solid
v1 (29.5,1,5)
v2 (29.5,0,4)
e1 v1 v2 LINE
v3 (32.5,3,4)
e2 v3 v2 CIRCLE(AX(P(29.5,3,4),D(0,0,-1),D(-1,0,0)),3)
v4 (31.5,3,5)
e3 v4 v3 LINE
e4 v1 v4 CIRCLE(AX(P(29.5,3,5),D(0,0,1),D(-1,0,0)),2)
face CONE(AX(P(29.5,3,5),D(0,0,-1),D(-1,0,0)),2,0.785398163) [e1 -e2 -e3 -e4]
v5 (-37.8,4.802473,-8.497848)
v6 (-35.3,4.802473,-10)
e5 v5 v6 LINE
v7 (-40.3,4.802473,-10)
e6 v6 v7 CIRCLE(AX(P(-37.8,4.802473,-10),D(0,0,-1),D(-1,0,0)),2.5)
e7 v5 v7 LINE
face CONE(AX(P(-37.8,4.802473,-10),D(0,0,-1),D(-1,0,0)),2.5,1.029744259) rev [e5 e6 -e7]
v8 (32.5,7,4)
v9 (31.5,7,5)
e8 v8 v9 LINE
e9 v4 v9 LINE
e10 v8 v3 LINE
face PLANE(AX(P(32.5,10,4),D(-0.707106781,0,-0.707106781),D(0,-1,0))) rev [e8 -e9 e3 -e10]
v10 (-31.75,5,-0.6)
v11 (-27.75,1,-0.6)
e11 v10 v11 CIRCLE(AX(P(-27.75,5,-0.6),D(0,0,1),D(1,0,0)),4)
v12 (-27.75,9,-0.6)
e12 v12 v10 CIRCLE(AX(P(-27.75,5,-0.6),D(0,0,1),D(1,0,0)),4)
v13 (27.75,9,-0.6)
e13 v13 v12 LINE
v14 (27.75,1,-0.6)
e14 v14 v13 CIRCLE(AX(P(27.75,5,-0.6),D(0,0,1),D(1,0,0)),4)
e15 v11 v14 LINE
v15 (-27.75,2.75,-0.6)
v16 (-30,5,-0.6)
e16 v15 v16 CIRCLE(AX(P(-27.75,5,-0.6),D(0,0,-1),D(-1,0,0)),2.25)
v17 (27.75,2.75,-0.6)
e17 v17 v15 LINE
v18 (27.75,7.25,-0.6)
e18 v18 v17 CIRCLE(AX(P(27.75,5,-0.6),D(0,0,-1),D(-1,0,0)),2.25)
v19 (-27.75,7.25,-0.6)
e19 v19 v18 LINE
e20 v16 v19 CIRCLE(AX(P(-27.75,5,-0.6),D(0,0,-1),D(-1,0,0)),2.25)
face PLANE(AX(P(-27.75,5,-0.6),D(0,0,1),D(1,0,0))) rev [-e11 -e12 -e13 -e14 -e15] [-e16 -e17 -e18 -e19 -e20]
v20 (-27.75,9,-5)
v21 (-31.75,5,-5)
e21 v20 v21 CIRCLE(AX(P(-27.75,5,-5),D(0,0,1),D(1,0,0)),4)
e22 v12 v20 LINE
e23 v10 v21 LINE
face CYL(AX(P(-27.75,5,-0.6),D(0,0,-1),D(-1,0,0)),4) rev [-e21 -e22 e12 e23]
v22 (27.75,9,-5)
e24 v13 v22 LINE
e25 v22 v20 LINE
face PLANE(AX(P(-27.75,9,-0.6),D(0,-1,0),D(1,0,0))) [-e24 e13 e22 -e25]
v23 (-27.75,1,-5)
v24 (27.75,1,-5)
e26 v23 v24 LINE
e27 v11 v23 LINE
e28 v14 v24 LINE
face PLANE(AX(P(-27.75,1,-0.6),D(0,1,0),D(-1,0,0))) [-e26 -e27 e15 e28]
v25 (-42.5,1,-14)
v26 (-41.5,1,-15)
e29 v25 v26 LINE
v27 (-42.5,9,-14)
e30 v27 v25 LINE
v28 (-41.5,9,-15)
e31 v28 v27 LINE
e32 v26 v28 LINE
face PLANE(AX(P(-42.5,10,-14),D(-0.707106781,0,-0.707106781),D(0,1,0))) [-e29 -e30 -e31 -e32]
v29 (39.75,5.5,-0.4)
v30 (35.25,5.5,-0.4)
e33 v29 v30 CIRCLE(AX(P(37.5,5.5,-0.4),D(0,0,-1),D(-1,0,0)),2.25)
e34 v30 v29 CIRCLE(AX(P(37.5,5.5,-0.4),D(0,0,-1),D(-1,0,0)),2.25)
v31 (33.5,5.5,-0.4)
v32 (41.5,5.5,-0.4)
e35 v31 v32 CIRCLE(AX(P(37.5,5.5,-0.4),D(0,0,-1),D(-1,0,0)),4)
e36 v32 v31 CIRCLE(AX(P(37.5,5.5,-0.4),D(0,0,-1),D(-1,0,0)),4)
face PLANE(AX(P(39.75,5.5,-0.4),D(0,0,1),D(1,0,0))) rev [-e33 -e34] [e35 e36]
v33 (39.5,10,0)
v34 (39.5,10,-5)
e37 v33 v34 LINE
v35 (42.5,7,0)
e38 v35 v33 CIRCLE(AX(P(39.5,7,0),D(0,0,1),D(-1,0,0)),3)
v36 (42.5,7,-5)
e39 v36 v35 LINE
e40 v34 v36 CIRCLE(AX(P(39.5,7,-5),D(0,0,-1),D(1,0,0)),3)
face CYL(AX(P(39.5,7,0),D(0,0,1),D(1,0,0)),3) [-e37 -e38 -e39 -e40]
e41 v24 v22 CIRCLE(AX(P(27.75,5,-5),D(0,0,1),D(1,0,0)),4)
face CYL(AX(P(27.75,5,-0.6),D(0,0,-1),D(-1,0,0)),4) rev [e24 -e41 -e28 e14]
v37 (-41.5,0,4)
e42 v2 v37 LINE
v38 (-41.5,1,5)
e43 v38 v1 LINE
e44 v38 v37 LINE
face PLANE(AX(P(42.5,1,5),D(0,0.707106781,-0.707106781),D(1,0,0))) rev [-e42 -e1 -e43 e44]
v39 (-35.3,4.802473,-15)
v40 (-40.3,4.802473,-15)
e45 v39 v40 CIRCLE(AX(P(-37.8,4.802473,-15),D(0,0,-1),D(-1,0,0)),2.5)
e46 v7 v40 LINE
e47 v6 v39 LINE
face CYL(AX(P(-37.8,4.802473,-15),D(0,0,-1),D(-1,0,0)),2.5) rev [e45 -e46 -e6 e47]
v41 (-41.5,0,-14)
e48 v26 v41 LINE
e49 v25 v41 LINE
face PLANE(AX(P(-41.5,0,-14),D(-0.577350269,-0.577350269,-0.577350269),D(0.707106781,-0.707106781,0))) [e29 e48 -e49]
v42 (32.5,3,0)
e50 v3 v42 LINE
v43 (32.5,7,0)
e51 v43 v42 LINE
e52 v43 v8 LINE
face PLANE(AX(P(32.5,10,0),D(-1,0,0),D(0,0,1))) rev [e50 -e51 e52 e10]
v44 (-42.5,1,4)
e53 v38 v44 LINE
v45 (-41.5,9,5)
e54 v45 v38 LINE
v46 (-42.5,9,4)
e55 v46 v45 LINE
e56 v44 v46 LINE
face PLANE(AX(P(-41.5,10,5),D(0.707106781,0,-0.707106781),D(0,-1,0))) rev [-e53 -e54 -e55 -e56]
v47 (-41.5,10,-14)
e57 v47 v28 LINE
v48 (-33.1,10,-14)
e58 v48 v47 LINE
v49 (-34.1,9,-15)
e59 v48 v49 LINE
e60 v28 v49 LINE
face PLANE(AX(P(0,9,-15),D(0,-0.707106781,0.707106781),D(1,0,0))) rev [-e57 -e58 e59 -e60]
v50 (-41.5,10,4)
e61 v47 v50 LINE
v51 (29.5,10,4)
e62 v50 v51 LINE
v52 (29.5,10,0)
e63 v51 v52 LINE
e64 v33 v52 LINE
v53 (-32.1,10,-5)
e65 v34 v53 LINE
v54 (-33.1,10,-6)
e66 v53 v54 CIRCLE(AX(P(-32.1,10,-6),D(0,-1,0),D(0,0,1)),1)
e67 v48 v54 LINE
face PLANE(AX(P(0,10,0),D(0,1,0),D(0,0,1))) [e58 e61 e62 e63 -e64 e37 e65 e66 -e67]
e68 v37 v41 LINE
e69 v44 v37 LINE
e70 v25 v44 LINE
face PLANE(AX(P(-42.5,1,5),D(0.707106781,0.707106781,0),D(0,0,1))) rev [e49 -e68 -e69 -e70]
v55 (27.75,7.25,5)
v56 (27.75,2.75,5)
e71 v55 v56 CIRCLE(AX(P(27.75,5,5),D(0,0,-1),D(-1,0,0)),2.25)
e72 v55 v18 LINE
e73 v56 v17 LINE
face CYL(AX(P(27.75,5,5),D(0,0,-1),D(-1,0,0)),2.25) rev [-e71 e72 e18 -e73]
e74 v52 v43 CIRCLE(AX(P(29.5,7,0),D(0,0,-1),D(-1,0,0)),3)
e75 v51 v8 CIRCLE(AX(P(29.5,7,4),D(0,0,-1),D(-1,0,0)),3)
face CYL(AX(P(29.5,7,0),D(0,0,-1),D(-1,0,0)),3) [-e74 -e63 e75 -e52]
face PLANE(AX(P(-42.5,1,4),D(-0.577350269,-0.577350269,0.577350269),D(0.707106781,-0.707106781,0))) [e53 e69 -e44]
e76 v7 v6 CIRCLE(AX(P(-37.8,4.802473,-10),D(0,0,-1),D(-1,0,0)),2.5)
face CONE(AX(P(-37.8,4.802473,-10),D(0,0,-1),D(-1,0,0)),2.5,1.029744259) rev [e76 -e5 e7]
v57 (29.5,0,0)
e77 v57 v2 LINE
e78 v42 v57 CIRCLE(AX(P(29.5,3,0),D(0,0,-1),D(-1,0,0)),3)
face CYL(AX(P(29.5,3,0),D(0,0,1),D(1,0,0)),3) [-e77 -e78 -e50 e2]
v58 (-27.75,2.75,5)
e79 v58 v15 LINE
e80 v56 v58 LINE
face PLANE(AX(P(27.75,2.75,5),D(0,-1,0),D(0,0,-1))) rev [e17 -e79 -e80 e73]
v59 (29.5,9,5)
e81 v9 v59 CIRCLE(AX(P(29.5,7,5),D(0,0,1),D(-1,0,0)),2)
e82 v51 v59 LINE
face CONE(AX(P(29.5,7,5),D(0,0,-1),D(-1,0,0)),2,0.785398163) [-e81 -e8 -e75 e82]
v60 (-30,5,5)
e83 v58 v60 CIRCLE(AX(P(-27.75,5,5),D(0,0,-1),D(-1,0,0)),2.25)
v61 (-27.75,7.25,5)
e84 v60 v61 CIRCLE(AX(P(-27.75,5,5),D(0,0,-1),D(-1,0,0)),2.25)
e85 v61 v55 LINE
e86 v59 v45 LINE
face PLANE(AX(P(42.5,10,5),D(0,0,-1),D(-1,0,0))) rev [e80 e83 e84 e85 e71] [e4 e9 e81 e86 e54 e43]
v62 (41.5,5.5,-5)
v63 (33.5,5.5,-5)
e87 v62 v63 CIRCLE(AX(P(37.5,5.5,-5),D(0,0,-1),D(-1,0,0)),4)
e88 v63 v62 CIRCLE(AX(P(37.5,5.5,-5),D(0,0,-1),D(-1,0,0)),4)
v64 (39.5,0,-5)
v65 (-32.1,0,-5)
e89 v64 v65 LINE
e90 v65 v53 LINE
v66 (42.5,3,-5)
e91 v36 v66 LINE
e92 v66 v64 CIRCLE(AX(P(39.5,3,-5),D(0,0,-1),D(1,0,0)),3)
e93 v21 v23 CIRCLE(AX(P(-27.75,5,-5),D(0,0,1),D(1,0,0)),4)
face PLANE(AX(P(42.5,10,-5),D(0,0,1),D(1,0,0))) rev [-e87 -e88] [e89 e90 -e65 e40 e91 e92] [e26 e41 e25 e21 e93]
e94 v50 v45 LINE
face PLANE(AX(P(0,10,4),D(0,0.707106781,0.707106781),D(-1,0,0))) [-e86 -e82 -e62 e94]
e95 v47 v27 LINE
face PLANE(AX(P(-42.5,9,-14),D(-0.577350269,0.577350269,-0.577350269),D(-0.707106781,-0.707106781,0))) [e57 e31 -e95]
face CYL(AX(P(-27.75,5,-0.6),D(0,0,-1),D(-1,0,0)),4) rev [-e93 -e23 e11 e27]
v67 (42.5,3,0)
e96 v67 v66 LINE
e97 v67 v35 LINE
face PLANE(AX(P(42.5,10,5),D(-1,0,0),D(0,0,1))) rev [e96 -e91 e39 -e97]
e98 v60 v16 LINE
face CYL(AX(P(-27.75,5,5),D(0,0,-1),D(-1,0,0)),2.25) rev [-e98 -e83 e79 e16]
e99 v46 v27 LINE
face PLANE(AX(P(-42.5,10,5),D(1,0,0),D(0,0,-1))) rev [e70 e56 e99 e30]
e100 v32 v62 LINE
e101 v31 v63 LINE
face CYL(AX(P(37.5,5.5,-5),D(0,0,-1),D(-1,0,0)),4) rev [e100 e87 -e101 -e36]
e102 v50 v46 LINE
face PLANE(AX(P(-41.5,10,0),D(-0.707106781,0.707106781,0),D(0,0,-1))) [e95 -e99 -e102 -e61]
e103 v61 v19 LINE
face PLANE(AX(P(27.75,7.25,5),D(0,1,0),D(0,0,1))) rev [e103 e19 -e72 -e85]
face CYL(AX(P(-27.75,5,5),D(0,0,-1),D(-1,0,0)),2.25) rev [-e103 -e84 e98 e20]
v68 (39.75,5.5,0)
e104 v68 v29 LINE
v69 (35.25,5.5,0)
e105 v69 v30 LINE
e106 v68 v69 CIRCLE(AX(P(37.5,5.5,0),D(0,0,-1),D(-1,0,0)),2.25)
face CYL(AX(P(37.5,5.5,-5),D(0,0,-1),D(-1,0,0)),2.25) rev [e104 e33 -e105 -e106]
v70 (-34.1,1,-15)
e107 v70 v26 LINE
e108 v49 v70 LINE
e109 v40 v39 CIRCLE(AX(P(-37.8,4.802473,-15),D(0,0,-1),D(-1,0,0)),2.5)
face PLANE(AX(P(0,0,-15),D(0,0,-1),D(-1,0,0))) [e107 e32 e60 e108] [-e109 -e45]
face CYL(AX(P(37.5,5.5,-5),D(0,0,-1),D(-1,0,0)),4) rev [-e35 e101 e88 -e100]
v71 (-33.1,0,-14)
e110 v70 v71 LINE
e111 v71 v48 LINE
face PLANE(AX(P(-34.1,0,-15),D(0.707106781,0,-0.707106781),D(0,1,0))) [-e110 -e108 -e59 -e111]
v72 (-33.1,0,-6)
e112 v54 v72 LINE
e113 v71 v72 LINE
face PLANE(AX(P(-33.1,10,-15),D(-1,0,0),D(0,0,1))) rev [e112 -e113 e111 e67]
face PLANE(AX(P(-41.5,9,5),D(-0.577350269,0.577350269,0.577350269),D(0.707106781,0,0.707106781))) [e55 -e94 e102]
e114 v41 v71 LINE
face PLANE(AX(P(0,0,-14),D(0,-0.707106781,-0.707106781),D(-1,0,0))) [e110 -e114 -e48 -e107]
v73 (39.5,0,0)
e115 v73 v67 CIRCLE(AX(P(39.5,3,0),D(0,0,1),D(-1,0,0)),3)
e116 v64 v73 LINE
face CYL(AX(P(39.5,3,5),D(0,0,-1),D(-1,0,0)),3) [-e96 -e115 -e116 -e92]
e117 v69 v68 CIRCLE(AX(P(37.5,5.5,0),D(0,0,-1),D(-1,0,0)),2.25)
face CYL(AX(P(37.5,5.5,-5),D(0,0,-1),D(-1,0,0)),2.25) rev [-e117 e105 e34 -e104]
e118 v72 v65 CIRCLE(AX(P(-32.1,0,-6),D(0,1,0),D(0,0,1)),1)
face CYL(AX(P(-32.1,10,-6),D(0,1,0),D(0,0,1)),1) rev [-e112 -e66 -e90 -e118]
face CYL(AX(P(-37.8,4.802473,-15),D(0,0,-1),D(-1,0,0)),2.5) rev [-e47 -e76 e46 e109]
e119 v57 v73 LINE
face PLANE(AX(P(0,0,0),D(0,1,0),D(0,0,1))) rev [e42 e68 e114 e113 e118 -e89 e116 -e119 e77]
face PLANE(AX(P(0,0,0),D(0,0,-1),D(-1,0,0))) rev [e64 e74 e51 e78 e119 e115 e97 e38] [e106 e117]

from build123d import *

# Parameters (mm, degrees)
SKETCH1_W                                            = 85
SKETCH1_H                                            = 10
BOSS_EXTRUDE1_DEPTH                                  = 10
CUT_EXTRUDE1_DEPTH                                   = 4.4
CUT_EXTRUDE2_DEPTH                                   = 45.018291652
SKETCH4_W                                            = 9.4
SKETCH4_H                                            = 10
BOSS_EXTRUDE2_DEPTH                                  = 10
SKETCH5_W                                            = 10
SKETCH5_H                                            = 10
CUT_EXTRUDE3_DEPTH                                   = 5
M6_TAPPED_HOLE1_D                                    = 5
M6_TAPPED_HOLE1_DEPTH                                = 5
M6_TAPPED_HOLE1_TIP                                  = 1.502151548
CBORE_FOR_M4_HEXAGON_SOCKET_HEAD_CAP_SCR_D           = 4.5
CBORE_FOR_M4_HEXAGON_SOCKET_HEAD_CAP_SCR_DEPTH       = 14
CBORE_FOR_M4_HEXAGON_SOCKET_HEAD_CAP_SCR_CBORE_D     = 8
CBORE_FOR_M4_HEXAGON_SOCKET_HEAD_CAP_SCR_CBORE_DEPTH = 4.6
CBORE_FOR_M4_HEXAGON_SOCKET_HEAD_CAP_SCR_TIP         = 1.351936393
FILLET1_R                                            = 3
FILLET2_R                                            = 1
CHAMFER1_SIZE                                        = 1


with BuildPart() as part:
    # Sketch1 → Boss-Extrude1 (new body)
    with BuildSketch(Plane(origin=(0, 0, 0), x_dir=(1, 0, 0), z_dir=(0, 1, 0))):
        Rectangle(SKETCH1_W, SKETCH1_H)
    extrude(amount=BOSS_EXTRUDE1_DEPTH)

    # Sketch2 → Cut-Extrude1 (cut)
    with BuildSketch(Plane.XY.offset(-5)):
        with BuildLine():
            Line((-27.75, 9), (27.75, 9))
            ThreePointArc((27.75, 9), (31.75, 5), (27.75, 1))
            Line((27.75, 1), (-27.75, 1))
            ThreePointArc((-27.75, 1), (-31.75, 5), (-27.75, 9))
        make_face()
    extrude(amount=CUT_EXTRUDE1_DEPTH, mode=Mode.SUBTRACT)

    # Sketch3 → Cut-Extrude2 (cut, through all)
    with BuildSketch(Plane(origin=(0, 0, -0.6), x_dir=(-1, 0, 0), z_dir=(0, 0, -1))):
        with BuildLine():
            Line((-27.75, 7.25), (27.75, 7.25))
            ThreePointArc((27.75, 7.25), (30, 5), (27.75, 2.75))
            Line((27.75, 2.75), (-27.75, 2.75))
            ThreePointArc((-27.75, 2.75), (-30, 5), (-27.75, 7.25))
        make_face()
    extrude(amount=-CUT_EXTRUDE2_DEPTH, mode=Mode.SUBTRACT)

    # Sketch4 → Boss-Extrude2 (add)
    with BuildSketch(Plane.XY.offset(-5)):
        with Locations((-37.8, 5)):
            Rectangle(SKETCH4_W, SKETCH4_H)
    extrude(amount=-BOSS_EXTRUDE2_DEPTH)

    # Sketch5 → Cut-Extrude3 (cut)
    with BuildSketch(Plane.XY.offset(5)):
        with Locations((37.5, 5)):
            Rectangle(SKETCH5_W, SKETCH5_H)
    extrude(amount=-CUT_EXTRUDE3_DEPTH, mode=Mode.SUBTRACT)

    # M6 Tapped Hole1
    with Locations(Plane(origin=(0, 0, -15), x_dir=(-1, 0, 0), z_dir=(0, 0, -1))):
        with Locations((37.8, 4.802472567)):
            Hole(M6_TAPPED_HOLE1_D / 2, depth=M6_TAPPED_HOLE1_DEPTH)
            with Locations((0, 0, -(M6_TAPPED_HOLE1_DEPTH + M6_TAPPED_HOLE1_TIP / 2))):  # 118° drill point
                Cone(0, M6_TAPPED_HOLE1_D / 2, M6_TAPPED_HOLE1_TIP, mode=Mode.SUBTRACT)

    # CBORE for M4 Hexagon socket head cap screws1
    with Locations(Plane(origin=(0, 0, -5), x_dir=(-1, 0, 0), z_dir=(0, 0, -1))):
        with Locations((-37.5, 5.5)):
            CounterBoreHole(CBORE_FOR_M4_HEXAGON_SOCKET_HEAD_CAP_SCR_D / 2, CBORE_FOR_M4_HEXAGON_SOCKET_HEAD_CAP_SCR_CBORE_D / 2, CBORE_FOR_M4_HEXAGON_SOCKET_HEAD_CAP_SCR_CBORE_DEPTH, depth=CBORE_FOR_M4_HEXAGON_SOCKET_HEAD_CAP_SCR_DEPTH)
            with Locations((0, 0, -(CBORE_FOR_M4_HEXAGON_SOCKET_HEAD_CAP_SCR_DEPTH + CBORE_FOR_M4_HEXAGON_SOCKET_HEAD_CAP_SCR_TIP / 2))):  # 118° drill point
                Cone(0, CBORE_FOR_M4_HEXAGON_SOCKET_HEAD_CAP_SCR_D / 2, CBORE_FOR_M4_HEXAGON_SOCKET_HEAD_CAP_SCR_TIP, mode=Mode.SUBTRACT)

    # Fillet1
    fillet1_edges = [part.edges().sort_by_distance(p)[0] for p in [
        (42.5, 0, -2.5),
        (42.5, 10, -2.5),
        (32.5, 0, 2.5),
        (32.5, 10, 2.5),
    ]]
    fillet(fillet1_edges, radius=FILLET1_R)

    # Fillet2
    fillet2_edges = [part.edges().sort_by_distance(p)[0] for p in [
        (-33.1, 5, -5),
    ]]
    fillet(fillet2_edges, radius=FILLET2_R)

    # Chamfer1
    chamfer1_edges = [part.edges().sort_by_distance(p)[0] for p in [
        (-37.8, 0, -15),
        (-42.5, 5, -15),
        (-37.8, 10, -15),
        (-33.1, 5, -15),
        (-42.5, 10, -5),
        (-6.5, 0, 5),
        (-42.5, 0, -5),
        (-42.5, 5, 5),
        (-6.5, 10, 5),
        (32.5, 5, 5),
        (31.621320344, 9.121320344, 5),
        (31.621320344, 0.878679656, 5),
    ]]
    chamfer(chamfer1_edges, length=CHAMFER1_SIZE)


solid = part.part
